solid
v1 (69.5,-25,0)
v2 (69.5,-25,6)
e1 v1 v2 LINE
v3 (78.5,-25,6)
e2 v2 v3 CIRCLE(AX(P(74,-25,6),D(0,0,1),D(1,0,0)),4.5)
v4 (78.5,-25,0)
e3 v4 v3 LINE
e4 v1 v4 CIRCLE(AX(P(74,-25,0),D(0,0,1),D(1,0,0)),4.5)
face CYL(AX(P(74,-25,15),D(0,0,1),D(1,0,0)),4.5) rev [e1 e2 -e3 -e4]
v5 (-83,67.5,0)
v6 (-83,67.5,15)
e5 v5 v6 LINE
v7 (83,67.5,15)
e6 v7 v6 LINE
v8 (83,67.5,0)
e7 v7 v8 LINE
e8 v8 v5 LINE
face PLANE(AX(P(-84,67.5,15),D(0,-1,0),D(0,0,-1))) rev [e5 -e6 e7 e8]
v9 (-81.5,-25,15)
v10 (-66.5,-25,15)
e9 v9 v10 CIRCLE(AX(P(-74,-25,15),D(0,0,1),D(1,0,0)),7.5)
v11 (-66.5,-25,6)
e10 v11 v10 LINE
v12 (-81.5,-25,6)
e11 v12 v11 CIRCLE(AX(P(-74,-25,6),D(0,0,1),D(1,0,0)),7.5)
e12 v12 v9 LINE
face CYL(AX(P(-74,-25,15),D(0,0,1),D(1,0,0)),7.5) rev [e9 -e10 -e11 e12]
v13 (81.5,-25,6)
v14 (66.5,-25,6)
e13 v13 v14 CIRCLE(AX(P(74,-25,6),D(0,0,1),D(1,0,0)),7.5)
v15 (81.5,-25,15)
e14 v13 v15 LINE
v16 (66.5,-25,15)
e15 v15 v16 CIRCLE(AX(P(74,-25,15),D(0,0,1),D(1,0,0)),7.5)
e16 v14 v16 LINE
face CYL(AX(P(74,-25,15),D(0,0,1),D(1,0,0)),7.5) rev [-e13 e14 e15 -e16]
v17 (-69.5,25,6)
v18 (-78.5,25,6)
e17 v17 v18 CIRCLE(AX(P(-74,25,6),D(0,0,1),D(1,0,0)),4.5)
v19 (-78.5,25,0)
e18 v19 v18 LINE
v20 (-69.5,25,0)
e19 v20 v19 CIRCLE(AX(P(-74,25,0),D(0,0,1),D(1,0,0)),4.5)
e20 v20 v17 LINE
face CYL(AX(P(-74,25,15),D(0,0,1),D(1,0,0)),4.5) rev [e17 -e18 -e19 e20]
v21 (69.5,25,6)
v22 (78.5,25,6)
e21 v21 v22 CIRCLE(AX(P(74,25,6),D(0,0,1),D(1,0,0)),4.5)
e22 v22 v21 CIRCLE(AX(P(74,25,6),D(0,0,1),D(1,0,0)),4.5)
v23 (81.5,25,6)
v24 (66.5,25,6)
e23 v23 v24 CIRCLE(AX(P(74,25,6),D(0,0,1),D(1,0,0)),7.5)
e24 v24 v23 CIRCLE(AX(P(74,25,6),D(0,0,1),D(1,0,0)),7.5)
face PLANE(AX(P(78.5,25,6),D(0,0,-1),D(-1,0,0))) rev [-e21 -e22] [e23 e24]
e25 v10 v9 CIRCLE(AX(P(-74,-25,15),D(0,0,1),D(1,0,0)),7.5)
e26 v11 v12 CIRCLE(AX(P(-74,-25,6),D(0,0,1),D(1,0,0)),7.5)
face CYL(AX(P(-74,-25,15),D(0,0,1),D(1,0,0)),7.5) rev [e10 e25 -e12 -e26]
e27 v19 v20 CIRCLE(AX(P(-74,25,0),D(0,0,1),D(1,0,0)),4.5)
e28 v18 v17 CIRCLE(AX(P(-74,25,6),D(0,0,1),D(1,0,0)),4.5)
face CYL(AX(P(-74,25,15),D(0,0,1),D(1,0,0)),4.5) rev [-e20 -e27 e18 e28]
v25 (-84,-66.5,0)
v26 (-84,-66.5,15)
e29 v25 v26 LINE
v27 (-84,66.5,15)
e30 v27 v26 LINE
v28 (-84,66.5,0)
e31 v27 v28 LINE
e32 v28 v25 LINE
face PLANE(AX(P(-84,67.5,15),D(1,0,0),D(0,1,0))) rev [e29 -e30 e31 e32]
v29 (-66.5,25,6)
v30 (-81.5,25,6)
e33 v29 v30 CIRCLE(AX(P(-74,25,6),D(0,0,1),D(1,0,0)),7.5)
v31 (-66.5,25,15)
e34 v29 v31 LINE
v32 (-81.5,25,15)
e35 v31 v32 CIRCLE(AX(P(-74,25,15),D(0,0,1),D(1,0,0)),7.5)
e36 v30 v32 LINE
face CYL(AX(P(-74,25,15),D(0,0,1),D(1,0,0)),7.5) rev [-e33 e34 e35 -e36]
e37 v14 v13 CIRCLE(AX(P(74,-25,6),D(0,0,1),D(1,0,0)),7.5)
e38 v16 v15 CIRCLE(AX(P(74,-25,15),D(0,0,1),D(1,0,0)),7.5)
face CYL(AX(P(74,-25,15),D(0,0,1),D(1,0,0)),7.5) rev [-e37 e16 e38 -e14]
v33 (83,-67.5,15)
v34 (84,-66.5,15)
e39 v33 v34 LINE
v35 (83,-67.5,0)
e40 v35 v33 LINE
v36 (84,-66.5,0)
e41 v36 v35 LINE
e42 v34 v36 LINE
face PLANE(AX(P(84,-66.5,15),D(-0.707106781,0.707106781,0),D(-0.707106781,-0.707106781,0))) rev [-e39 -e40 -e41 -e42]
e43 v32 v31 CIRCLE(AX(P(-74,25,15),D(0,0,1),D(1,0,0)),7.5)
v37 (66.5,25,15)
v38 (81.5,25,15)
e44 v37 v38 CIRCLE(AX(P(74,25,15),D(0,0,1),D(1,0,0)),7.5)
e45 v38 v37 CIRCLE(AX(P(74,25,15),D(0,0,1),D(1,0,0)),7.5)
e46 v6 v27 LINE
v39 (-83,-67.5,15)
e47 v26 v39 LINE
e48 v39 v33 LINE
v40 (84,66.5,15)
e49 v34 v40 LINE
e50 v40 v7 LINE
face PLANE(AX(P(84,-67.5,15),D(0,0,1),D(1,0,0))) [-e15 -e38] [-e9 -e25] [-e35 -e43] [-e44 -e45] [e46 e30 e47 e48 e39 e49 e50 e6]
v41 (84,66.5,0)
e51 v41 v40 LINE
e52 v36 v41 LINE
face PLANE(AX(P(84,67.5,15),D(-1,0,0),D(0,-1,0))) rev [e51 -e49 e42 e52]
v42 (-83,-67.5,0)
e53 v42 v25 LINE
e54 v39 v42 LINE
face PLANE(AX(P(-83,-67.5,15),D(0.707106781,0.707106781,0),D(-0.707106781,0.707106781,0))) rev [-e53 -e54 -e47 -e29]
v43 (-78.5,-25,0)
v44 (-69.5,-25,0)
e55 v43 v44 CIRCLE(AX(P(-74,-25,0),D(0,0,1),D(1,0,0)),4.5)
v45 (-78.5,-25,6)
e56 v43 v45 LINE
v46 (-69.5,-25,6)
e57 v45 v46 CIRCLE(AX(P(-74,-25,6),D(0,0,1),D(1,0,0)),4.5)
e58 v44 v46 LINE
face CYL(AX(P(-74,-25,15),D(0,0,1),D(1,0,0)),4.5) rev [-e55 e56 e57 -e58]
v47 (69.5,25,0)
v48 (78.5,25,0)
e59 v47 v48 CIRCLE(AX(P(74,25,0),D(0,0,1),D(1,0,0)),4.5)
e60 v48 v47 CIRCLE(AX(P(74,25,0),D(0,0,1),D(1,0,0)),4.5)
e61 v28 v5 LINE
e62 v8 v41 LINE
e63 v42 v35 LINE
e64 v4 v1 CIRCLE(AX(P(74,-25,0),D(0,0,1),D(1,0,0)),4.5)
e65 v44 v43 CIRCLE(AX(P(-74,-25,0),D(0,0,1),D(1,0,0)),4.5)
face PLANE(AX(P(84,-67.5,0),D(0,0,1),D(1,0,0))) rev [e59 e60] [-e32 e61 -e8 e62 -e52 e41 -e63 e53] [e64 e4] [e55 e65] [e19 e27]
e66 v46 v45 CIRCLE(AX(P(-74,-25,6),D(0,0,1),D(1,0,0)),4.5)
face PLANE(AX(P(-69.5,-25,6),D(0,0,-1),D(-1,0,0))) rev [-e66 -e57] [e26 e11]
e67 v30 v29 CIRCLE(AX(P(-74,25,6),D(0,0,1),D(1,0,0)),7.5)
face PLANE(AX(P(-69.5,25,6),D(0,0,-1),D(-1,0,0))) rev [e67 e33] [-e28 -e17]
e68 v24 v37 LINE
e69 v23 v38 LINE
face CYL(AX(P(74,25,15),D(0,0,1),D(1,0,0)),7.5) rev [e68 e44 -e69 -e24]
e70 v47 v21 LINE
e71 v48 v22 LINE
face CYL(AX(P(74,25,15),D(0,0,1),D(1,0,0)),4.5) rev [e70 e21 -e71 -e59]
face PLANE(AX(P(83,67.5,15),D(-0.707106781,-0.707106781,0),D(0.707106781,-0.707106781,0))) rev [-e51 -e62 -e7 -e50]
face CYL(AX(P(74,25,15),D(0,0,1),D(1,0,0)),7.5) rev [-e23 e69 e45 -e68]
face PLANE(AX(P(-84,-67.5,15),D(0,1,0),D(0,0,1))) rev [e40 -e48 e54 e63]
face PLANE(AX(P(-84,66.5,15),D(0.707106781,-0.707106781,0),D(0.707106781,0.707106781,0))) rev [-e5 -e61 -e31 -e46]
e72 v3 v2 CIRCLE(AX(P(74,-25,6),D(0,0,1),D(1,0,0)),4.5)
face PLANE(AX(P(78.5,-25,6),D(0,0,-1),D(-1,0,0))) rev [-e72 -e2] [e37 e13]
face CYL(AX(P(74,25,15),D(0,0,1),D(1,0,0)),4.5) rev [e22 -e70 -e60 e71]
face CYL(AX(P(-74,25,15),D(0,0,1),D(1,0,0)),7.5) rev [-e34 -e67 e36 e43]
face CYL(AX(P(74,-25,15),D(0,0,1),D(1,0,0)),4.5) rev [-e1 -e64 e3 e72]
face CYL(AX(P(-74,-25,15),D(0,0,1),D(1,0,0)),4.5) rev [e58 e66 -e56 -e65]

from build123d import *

# Parameters (mm, degrees)
SKETCH1_W                                            = 168
SKETCH1_H                                            = 135
BOSS_EXTRUDE1_DEPTH                                  = 15
HOLE_SIZE_PER_SOCKET_HEAD_CAP_SCREW_TYPE_D           = 9
HOLE_SIZE_PER_SOCKET_HEAD_CAP_SCREW_TYPE_CBORE_D     = 15
HOLE_SIZE_PER_SOCKET_HEAD_CAP_SCREW_TYPE_CBORE_DEPTH = 9
CHAMFER1_SIZE                                        = 1


with BuildPart() as part:
    # Sketch1 → Boss-Extrude1 (new body)
    with BuildSketch(Plane.XY):
        Rectangle(SKETCH1_W, SKETCH1_H)
    extrude(amount=BOSS_EXTRUDE1_DEPTH)

    # Hole size per socket head cap screw type1 (through all)
    with Locations(Plane.XY.offset(15)):
        with Locations((-74, 25), (-74, -25), (74, -25), (74, 25)):
            CounterBoreHole(HOLE_SIZE_PER_SOCKET_HEAD_CAP_SCREW_TYPE_D / 2, HOLE_SIZE_PER_SOCKET_HEAD_CAP_SCREW_TYPE_CBORE_D / 2, HOLE_SIZE_PER_SOCKET_HEAD_CAP_SCREW_TYPE_CBORE_DEPTH)

    # Chamfer1
    chamfer1_edges = [part.edges().sort_by_distance(p)[0] for p in [
        (84, -67.5, 7.5),
        (-84, -67.5, 7.5),
        (-84, 67.5, 7.5),
        (84, 67.5, 7.5),
    ]]
    chamfer(chamfer1_edges, length=CHAMFER1_SIZE)


solid = part.part
